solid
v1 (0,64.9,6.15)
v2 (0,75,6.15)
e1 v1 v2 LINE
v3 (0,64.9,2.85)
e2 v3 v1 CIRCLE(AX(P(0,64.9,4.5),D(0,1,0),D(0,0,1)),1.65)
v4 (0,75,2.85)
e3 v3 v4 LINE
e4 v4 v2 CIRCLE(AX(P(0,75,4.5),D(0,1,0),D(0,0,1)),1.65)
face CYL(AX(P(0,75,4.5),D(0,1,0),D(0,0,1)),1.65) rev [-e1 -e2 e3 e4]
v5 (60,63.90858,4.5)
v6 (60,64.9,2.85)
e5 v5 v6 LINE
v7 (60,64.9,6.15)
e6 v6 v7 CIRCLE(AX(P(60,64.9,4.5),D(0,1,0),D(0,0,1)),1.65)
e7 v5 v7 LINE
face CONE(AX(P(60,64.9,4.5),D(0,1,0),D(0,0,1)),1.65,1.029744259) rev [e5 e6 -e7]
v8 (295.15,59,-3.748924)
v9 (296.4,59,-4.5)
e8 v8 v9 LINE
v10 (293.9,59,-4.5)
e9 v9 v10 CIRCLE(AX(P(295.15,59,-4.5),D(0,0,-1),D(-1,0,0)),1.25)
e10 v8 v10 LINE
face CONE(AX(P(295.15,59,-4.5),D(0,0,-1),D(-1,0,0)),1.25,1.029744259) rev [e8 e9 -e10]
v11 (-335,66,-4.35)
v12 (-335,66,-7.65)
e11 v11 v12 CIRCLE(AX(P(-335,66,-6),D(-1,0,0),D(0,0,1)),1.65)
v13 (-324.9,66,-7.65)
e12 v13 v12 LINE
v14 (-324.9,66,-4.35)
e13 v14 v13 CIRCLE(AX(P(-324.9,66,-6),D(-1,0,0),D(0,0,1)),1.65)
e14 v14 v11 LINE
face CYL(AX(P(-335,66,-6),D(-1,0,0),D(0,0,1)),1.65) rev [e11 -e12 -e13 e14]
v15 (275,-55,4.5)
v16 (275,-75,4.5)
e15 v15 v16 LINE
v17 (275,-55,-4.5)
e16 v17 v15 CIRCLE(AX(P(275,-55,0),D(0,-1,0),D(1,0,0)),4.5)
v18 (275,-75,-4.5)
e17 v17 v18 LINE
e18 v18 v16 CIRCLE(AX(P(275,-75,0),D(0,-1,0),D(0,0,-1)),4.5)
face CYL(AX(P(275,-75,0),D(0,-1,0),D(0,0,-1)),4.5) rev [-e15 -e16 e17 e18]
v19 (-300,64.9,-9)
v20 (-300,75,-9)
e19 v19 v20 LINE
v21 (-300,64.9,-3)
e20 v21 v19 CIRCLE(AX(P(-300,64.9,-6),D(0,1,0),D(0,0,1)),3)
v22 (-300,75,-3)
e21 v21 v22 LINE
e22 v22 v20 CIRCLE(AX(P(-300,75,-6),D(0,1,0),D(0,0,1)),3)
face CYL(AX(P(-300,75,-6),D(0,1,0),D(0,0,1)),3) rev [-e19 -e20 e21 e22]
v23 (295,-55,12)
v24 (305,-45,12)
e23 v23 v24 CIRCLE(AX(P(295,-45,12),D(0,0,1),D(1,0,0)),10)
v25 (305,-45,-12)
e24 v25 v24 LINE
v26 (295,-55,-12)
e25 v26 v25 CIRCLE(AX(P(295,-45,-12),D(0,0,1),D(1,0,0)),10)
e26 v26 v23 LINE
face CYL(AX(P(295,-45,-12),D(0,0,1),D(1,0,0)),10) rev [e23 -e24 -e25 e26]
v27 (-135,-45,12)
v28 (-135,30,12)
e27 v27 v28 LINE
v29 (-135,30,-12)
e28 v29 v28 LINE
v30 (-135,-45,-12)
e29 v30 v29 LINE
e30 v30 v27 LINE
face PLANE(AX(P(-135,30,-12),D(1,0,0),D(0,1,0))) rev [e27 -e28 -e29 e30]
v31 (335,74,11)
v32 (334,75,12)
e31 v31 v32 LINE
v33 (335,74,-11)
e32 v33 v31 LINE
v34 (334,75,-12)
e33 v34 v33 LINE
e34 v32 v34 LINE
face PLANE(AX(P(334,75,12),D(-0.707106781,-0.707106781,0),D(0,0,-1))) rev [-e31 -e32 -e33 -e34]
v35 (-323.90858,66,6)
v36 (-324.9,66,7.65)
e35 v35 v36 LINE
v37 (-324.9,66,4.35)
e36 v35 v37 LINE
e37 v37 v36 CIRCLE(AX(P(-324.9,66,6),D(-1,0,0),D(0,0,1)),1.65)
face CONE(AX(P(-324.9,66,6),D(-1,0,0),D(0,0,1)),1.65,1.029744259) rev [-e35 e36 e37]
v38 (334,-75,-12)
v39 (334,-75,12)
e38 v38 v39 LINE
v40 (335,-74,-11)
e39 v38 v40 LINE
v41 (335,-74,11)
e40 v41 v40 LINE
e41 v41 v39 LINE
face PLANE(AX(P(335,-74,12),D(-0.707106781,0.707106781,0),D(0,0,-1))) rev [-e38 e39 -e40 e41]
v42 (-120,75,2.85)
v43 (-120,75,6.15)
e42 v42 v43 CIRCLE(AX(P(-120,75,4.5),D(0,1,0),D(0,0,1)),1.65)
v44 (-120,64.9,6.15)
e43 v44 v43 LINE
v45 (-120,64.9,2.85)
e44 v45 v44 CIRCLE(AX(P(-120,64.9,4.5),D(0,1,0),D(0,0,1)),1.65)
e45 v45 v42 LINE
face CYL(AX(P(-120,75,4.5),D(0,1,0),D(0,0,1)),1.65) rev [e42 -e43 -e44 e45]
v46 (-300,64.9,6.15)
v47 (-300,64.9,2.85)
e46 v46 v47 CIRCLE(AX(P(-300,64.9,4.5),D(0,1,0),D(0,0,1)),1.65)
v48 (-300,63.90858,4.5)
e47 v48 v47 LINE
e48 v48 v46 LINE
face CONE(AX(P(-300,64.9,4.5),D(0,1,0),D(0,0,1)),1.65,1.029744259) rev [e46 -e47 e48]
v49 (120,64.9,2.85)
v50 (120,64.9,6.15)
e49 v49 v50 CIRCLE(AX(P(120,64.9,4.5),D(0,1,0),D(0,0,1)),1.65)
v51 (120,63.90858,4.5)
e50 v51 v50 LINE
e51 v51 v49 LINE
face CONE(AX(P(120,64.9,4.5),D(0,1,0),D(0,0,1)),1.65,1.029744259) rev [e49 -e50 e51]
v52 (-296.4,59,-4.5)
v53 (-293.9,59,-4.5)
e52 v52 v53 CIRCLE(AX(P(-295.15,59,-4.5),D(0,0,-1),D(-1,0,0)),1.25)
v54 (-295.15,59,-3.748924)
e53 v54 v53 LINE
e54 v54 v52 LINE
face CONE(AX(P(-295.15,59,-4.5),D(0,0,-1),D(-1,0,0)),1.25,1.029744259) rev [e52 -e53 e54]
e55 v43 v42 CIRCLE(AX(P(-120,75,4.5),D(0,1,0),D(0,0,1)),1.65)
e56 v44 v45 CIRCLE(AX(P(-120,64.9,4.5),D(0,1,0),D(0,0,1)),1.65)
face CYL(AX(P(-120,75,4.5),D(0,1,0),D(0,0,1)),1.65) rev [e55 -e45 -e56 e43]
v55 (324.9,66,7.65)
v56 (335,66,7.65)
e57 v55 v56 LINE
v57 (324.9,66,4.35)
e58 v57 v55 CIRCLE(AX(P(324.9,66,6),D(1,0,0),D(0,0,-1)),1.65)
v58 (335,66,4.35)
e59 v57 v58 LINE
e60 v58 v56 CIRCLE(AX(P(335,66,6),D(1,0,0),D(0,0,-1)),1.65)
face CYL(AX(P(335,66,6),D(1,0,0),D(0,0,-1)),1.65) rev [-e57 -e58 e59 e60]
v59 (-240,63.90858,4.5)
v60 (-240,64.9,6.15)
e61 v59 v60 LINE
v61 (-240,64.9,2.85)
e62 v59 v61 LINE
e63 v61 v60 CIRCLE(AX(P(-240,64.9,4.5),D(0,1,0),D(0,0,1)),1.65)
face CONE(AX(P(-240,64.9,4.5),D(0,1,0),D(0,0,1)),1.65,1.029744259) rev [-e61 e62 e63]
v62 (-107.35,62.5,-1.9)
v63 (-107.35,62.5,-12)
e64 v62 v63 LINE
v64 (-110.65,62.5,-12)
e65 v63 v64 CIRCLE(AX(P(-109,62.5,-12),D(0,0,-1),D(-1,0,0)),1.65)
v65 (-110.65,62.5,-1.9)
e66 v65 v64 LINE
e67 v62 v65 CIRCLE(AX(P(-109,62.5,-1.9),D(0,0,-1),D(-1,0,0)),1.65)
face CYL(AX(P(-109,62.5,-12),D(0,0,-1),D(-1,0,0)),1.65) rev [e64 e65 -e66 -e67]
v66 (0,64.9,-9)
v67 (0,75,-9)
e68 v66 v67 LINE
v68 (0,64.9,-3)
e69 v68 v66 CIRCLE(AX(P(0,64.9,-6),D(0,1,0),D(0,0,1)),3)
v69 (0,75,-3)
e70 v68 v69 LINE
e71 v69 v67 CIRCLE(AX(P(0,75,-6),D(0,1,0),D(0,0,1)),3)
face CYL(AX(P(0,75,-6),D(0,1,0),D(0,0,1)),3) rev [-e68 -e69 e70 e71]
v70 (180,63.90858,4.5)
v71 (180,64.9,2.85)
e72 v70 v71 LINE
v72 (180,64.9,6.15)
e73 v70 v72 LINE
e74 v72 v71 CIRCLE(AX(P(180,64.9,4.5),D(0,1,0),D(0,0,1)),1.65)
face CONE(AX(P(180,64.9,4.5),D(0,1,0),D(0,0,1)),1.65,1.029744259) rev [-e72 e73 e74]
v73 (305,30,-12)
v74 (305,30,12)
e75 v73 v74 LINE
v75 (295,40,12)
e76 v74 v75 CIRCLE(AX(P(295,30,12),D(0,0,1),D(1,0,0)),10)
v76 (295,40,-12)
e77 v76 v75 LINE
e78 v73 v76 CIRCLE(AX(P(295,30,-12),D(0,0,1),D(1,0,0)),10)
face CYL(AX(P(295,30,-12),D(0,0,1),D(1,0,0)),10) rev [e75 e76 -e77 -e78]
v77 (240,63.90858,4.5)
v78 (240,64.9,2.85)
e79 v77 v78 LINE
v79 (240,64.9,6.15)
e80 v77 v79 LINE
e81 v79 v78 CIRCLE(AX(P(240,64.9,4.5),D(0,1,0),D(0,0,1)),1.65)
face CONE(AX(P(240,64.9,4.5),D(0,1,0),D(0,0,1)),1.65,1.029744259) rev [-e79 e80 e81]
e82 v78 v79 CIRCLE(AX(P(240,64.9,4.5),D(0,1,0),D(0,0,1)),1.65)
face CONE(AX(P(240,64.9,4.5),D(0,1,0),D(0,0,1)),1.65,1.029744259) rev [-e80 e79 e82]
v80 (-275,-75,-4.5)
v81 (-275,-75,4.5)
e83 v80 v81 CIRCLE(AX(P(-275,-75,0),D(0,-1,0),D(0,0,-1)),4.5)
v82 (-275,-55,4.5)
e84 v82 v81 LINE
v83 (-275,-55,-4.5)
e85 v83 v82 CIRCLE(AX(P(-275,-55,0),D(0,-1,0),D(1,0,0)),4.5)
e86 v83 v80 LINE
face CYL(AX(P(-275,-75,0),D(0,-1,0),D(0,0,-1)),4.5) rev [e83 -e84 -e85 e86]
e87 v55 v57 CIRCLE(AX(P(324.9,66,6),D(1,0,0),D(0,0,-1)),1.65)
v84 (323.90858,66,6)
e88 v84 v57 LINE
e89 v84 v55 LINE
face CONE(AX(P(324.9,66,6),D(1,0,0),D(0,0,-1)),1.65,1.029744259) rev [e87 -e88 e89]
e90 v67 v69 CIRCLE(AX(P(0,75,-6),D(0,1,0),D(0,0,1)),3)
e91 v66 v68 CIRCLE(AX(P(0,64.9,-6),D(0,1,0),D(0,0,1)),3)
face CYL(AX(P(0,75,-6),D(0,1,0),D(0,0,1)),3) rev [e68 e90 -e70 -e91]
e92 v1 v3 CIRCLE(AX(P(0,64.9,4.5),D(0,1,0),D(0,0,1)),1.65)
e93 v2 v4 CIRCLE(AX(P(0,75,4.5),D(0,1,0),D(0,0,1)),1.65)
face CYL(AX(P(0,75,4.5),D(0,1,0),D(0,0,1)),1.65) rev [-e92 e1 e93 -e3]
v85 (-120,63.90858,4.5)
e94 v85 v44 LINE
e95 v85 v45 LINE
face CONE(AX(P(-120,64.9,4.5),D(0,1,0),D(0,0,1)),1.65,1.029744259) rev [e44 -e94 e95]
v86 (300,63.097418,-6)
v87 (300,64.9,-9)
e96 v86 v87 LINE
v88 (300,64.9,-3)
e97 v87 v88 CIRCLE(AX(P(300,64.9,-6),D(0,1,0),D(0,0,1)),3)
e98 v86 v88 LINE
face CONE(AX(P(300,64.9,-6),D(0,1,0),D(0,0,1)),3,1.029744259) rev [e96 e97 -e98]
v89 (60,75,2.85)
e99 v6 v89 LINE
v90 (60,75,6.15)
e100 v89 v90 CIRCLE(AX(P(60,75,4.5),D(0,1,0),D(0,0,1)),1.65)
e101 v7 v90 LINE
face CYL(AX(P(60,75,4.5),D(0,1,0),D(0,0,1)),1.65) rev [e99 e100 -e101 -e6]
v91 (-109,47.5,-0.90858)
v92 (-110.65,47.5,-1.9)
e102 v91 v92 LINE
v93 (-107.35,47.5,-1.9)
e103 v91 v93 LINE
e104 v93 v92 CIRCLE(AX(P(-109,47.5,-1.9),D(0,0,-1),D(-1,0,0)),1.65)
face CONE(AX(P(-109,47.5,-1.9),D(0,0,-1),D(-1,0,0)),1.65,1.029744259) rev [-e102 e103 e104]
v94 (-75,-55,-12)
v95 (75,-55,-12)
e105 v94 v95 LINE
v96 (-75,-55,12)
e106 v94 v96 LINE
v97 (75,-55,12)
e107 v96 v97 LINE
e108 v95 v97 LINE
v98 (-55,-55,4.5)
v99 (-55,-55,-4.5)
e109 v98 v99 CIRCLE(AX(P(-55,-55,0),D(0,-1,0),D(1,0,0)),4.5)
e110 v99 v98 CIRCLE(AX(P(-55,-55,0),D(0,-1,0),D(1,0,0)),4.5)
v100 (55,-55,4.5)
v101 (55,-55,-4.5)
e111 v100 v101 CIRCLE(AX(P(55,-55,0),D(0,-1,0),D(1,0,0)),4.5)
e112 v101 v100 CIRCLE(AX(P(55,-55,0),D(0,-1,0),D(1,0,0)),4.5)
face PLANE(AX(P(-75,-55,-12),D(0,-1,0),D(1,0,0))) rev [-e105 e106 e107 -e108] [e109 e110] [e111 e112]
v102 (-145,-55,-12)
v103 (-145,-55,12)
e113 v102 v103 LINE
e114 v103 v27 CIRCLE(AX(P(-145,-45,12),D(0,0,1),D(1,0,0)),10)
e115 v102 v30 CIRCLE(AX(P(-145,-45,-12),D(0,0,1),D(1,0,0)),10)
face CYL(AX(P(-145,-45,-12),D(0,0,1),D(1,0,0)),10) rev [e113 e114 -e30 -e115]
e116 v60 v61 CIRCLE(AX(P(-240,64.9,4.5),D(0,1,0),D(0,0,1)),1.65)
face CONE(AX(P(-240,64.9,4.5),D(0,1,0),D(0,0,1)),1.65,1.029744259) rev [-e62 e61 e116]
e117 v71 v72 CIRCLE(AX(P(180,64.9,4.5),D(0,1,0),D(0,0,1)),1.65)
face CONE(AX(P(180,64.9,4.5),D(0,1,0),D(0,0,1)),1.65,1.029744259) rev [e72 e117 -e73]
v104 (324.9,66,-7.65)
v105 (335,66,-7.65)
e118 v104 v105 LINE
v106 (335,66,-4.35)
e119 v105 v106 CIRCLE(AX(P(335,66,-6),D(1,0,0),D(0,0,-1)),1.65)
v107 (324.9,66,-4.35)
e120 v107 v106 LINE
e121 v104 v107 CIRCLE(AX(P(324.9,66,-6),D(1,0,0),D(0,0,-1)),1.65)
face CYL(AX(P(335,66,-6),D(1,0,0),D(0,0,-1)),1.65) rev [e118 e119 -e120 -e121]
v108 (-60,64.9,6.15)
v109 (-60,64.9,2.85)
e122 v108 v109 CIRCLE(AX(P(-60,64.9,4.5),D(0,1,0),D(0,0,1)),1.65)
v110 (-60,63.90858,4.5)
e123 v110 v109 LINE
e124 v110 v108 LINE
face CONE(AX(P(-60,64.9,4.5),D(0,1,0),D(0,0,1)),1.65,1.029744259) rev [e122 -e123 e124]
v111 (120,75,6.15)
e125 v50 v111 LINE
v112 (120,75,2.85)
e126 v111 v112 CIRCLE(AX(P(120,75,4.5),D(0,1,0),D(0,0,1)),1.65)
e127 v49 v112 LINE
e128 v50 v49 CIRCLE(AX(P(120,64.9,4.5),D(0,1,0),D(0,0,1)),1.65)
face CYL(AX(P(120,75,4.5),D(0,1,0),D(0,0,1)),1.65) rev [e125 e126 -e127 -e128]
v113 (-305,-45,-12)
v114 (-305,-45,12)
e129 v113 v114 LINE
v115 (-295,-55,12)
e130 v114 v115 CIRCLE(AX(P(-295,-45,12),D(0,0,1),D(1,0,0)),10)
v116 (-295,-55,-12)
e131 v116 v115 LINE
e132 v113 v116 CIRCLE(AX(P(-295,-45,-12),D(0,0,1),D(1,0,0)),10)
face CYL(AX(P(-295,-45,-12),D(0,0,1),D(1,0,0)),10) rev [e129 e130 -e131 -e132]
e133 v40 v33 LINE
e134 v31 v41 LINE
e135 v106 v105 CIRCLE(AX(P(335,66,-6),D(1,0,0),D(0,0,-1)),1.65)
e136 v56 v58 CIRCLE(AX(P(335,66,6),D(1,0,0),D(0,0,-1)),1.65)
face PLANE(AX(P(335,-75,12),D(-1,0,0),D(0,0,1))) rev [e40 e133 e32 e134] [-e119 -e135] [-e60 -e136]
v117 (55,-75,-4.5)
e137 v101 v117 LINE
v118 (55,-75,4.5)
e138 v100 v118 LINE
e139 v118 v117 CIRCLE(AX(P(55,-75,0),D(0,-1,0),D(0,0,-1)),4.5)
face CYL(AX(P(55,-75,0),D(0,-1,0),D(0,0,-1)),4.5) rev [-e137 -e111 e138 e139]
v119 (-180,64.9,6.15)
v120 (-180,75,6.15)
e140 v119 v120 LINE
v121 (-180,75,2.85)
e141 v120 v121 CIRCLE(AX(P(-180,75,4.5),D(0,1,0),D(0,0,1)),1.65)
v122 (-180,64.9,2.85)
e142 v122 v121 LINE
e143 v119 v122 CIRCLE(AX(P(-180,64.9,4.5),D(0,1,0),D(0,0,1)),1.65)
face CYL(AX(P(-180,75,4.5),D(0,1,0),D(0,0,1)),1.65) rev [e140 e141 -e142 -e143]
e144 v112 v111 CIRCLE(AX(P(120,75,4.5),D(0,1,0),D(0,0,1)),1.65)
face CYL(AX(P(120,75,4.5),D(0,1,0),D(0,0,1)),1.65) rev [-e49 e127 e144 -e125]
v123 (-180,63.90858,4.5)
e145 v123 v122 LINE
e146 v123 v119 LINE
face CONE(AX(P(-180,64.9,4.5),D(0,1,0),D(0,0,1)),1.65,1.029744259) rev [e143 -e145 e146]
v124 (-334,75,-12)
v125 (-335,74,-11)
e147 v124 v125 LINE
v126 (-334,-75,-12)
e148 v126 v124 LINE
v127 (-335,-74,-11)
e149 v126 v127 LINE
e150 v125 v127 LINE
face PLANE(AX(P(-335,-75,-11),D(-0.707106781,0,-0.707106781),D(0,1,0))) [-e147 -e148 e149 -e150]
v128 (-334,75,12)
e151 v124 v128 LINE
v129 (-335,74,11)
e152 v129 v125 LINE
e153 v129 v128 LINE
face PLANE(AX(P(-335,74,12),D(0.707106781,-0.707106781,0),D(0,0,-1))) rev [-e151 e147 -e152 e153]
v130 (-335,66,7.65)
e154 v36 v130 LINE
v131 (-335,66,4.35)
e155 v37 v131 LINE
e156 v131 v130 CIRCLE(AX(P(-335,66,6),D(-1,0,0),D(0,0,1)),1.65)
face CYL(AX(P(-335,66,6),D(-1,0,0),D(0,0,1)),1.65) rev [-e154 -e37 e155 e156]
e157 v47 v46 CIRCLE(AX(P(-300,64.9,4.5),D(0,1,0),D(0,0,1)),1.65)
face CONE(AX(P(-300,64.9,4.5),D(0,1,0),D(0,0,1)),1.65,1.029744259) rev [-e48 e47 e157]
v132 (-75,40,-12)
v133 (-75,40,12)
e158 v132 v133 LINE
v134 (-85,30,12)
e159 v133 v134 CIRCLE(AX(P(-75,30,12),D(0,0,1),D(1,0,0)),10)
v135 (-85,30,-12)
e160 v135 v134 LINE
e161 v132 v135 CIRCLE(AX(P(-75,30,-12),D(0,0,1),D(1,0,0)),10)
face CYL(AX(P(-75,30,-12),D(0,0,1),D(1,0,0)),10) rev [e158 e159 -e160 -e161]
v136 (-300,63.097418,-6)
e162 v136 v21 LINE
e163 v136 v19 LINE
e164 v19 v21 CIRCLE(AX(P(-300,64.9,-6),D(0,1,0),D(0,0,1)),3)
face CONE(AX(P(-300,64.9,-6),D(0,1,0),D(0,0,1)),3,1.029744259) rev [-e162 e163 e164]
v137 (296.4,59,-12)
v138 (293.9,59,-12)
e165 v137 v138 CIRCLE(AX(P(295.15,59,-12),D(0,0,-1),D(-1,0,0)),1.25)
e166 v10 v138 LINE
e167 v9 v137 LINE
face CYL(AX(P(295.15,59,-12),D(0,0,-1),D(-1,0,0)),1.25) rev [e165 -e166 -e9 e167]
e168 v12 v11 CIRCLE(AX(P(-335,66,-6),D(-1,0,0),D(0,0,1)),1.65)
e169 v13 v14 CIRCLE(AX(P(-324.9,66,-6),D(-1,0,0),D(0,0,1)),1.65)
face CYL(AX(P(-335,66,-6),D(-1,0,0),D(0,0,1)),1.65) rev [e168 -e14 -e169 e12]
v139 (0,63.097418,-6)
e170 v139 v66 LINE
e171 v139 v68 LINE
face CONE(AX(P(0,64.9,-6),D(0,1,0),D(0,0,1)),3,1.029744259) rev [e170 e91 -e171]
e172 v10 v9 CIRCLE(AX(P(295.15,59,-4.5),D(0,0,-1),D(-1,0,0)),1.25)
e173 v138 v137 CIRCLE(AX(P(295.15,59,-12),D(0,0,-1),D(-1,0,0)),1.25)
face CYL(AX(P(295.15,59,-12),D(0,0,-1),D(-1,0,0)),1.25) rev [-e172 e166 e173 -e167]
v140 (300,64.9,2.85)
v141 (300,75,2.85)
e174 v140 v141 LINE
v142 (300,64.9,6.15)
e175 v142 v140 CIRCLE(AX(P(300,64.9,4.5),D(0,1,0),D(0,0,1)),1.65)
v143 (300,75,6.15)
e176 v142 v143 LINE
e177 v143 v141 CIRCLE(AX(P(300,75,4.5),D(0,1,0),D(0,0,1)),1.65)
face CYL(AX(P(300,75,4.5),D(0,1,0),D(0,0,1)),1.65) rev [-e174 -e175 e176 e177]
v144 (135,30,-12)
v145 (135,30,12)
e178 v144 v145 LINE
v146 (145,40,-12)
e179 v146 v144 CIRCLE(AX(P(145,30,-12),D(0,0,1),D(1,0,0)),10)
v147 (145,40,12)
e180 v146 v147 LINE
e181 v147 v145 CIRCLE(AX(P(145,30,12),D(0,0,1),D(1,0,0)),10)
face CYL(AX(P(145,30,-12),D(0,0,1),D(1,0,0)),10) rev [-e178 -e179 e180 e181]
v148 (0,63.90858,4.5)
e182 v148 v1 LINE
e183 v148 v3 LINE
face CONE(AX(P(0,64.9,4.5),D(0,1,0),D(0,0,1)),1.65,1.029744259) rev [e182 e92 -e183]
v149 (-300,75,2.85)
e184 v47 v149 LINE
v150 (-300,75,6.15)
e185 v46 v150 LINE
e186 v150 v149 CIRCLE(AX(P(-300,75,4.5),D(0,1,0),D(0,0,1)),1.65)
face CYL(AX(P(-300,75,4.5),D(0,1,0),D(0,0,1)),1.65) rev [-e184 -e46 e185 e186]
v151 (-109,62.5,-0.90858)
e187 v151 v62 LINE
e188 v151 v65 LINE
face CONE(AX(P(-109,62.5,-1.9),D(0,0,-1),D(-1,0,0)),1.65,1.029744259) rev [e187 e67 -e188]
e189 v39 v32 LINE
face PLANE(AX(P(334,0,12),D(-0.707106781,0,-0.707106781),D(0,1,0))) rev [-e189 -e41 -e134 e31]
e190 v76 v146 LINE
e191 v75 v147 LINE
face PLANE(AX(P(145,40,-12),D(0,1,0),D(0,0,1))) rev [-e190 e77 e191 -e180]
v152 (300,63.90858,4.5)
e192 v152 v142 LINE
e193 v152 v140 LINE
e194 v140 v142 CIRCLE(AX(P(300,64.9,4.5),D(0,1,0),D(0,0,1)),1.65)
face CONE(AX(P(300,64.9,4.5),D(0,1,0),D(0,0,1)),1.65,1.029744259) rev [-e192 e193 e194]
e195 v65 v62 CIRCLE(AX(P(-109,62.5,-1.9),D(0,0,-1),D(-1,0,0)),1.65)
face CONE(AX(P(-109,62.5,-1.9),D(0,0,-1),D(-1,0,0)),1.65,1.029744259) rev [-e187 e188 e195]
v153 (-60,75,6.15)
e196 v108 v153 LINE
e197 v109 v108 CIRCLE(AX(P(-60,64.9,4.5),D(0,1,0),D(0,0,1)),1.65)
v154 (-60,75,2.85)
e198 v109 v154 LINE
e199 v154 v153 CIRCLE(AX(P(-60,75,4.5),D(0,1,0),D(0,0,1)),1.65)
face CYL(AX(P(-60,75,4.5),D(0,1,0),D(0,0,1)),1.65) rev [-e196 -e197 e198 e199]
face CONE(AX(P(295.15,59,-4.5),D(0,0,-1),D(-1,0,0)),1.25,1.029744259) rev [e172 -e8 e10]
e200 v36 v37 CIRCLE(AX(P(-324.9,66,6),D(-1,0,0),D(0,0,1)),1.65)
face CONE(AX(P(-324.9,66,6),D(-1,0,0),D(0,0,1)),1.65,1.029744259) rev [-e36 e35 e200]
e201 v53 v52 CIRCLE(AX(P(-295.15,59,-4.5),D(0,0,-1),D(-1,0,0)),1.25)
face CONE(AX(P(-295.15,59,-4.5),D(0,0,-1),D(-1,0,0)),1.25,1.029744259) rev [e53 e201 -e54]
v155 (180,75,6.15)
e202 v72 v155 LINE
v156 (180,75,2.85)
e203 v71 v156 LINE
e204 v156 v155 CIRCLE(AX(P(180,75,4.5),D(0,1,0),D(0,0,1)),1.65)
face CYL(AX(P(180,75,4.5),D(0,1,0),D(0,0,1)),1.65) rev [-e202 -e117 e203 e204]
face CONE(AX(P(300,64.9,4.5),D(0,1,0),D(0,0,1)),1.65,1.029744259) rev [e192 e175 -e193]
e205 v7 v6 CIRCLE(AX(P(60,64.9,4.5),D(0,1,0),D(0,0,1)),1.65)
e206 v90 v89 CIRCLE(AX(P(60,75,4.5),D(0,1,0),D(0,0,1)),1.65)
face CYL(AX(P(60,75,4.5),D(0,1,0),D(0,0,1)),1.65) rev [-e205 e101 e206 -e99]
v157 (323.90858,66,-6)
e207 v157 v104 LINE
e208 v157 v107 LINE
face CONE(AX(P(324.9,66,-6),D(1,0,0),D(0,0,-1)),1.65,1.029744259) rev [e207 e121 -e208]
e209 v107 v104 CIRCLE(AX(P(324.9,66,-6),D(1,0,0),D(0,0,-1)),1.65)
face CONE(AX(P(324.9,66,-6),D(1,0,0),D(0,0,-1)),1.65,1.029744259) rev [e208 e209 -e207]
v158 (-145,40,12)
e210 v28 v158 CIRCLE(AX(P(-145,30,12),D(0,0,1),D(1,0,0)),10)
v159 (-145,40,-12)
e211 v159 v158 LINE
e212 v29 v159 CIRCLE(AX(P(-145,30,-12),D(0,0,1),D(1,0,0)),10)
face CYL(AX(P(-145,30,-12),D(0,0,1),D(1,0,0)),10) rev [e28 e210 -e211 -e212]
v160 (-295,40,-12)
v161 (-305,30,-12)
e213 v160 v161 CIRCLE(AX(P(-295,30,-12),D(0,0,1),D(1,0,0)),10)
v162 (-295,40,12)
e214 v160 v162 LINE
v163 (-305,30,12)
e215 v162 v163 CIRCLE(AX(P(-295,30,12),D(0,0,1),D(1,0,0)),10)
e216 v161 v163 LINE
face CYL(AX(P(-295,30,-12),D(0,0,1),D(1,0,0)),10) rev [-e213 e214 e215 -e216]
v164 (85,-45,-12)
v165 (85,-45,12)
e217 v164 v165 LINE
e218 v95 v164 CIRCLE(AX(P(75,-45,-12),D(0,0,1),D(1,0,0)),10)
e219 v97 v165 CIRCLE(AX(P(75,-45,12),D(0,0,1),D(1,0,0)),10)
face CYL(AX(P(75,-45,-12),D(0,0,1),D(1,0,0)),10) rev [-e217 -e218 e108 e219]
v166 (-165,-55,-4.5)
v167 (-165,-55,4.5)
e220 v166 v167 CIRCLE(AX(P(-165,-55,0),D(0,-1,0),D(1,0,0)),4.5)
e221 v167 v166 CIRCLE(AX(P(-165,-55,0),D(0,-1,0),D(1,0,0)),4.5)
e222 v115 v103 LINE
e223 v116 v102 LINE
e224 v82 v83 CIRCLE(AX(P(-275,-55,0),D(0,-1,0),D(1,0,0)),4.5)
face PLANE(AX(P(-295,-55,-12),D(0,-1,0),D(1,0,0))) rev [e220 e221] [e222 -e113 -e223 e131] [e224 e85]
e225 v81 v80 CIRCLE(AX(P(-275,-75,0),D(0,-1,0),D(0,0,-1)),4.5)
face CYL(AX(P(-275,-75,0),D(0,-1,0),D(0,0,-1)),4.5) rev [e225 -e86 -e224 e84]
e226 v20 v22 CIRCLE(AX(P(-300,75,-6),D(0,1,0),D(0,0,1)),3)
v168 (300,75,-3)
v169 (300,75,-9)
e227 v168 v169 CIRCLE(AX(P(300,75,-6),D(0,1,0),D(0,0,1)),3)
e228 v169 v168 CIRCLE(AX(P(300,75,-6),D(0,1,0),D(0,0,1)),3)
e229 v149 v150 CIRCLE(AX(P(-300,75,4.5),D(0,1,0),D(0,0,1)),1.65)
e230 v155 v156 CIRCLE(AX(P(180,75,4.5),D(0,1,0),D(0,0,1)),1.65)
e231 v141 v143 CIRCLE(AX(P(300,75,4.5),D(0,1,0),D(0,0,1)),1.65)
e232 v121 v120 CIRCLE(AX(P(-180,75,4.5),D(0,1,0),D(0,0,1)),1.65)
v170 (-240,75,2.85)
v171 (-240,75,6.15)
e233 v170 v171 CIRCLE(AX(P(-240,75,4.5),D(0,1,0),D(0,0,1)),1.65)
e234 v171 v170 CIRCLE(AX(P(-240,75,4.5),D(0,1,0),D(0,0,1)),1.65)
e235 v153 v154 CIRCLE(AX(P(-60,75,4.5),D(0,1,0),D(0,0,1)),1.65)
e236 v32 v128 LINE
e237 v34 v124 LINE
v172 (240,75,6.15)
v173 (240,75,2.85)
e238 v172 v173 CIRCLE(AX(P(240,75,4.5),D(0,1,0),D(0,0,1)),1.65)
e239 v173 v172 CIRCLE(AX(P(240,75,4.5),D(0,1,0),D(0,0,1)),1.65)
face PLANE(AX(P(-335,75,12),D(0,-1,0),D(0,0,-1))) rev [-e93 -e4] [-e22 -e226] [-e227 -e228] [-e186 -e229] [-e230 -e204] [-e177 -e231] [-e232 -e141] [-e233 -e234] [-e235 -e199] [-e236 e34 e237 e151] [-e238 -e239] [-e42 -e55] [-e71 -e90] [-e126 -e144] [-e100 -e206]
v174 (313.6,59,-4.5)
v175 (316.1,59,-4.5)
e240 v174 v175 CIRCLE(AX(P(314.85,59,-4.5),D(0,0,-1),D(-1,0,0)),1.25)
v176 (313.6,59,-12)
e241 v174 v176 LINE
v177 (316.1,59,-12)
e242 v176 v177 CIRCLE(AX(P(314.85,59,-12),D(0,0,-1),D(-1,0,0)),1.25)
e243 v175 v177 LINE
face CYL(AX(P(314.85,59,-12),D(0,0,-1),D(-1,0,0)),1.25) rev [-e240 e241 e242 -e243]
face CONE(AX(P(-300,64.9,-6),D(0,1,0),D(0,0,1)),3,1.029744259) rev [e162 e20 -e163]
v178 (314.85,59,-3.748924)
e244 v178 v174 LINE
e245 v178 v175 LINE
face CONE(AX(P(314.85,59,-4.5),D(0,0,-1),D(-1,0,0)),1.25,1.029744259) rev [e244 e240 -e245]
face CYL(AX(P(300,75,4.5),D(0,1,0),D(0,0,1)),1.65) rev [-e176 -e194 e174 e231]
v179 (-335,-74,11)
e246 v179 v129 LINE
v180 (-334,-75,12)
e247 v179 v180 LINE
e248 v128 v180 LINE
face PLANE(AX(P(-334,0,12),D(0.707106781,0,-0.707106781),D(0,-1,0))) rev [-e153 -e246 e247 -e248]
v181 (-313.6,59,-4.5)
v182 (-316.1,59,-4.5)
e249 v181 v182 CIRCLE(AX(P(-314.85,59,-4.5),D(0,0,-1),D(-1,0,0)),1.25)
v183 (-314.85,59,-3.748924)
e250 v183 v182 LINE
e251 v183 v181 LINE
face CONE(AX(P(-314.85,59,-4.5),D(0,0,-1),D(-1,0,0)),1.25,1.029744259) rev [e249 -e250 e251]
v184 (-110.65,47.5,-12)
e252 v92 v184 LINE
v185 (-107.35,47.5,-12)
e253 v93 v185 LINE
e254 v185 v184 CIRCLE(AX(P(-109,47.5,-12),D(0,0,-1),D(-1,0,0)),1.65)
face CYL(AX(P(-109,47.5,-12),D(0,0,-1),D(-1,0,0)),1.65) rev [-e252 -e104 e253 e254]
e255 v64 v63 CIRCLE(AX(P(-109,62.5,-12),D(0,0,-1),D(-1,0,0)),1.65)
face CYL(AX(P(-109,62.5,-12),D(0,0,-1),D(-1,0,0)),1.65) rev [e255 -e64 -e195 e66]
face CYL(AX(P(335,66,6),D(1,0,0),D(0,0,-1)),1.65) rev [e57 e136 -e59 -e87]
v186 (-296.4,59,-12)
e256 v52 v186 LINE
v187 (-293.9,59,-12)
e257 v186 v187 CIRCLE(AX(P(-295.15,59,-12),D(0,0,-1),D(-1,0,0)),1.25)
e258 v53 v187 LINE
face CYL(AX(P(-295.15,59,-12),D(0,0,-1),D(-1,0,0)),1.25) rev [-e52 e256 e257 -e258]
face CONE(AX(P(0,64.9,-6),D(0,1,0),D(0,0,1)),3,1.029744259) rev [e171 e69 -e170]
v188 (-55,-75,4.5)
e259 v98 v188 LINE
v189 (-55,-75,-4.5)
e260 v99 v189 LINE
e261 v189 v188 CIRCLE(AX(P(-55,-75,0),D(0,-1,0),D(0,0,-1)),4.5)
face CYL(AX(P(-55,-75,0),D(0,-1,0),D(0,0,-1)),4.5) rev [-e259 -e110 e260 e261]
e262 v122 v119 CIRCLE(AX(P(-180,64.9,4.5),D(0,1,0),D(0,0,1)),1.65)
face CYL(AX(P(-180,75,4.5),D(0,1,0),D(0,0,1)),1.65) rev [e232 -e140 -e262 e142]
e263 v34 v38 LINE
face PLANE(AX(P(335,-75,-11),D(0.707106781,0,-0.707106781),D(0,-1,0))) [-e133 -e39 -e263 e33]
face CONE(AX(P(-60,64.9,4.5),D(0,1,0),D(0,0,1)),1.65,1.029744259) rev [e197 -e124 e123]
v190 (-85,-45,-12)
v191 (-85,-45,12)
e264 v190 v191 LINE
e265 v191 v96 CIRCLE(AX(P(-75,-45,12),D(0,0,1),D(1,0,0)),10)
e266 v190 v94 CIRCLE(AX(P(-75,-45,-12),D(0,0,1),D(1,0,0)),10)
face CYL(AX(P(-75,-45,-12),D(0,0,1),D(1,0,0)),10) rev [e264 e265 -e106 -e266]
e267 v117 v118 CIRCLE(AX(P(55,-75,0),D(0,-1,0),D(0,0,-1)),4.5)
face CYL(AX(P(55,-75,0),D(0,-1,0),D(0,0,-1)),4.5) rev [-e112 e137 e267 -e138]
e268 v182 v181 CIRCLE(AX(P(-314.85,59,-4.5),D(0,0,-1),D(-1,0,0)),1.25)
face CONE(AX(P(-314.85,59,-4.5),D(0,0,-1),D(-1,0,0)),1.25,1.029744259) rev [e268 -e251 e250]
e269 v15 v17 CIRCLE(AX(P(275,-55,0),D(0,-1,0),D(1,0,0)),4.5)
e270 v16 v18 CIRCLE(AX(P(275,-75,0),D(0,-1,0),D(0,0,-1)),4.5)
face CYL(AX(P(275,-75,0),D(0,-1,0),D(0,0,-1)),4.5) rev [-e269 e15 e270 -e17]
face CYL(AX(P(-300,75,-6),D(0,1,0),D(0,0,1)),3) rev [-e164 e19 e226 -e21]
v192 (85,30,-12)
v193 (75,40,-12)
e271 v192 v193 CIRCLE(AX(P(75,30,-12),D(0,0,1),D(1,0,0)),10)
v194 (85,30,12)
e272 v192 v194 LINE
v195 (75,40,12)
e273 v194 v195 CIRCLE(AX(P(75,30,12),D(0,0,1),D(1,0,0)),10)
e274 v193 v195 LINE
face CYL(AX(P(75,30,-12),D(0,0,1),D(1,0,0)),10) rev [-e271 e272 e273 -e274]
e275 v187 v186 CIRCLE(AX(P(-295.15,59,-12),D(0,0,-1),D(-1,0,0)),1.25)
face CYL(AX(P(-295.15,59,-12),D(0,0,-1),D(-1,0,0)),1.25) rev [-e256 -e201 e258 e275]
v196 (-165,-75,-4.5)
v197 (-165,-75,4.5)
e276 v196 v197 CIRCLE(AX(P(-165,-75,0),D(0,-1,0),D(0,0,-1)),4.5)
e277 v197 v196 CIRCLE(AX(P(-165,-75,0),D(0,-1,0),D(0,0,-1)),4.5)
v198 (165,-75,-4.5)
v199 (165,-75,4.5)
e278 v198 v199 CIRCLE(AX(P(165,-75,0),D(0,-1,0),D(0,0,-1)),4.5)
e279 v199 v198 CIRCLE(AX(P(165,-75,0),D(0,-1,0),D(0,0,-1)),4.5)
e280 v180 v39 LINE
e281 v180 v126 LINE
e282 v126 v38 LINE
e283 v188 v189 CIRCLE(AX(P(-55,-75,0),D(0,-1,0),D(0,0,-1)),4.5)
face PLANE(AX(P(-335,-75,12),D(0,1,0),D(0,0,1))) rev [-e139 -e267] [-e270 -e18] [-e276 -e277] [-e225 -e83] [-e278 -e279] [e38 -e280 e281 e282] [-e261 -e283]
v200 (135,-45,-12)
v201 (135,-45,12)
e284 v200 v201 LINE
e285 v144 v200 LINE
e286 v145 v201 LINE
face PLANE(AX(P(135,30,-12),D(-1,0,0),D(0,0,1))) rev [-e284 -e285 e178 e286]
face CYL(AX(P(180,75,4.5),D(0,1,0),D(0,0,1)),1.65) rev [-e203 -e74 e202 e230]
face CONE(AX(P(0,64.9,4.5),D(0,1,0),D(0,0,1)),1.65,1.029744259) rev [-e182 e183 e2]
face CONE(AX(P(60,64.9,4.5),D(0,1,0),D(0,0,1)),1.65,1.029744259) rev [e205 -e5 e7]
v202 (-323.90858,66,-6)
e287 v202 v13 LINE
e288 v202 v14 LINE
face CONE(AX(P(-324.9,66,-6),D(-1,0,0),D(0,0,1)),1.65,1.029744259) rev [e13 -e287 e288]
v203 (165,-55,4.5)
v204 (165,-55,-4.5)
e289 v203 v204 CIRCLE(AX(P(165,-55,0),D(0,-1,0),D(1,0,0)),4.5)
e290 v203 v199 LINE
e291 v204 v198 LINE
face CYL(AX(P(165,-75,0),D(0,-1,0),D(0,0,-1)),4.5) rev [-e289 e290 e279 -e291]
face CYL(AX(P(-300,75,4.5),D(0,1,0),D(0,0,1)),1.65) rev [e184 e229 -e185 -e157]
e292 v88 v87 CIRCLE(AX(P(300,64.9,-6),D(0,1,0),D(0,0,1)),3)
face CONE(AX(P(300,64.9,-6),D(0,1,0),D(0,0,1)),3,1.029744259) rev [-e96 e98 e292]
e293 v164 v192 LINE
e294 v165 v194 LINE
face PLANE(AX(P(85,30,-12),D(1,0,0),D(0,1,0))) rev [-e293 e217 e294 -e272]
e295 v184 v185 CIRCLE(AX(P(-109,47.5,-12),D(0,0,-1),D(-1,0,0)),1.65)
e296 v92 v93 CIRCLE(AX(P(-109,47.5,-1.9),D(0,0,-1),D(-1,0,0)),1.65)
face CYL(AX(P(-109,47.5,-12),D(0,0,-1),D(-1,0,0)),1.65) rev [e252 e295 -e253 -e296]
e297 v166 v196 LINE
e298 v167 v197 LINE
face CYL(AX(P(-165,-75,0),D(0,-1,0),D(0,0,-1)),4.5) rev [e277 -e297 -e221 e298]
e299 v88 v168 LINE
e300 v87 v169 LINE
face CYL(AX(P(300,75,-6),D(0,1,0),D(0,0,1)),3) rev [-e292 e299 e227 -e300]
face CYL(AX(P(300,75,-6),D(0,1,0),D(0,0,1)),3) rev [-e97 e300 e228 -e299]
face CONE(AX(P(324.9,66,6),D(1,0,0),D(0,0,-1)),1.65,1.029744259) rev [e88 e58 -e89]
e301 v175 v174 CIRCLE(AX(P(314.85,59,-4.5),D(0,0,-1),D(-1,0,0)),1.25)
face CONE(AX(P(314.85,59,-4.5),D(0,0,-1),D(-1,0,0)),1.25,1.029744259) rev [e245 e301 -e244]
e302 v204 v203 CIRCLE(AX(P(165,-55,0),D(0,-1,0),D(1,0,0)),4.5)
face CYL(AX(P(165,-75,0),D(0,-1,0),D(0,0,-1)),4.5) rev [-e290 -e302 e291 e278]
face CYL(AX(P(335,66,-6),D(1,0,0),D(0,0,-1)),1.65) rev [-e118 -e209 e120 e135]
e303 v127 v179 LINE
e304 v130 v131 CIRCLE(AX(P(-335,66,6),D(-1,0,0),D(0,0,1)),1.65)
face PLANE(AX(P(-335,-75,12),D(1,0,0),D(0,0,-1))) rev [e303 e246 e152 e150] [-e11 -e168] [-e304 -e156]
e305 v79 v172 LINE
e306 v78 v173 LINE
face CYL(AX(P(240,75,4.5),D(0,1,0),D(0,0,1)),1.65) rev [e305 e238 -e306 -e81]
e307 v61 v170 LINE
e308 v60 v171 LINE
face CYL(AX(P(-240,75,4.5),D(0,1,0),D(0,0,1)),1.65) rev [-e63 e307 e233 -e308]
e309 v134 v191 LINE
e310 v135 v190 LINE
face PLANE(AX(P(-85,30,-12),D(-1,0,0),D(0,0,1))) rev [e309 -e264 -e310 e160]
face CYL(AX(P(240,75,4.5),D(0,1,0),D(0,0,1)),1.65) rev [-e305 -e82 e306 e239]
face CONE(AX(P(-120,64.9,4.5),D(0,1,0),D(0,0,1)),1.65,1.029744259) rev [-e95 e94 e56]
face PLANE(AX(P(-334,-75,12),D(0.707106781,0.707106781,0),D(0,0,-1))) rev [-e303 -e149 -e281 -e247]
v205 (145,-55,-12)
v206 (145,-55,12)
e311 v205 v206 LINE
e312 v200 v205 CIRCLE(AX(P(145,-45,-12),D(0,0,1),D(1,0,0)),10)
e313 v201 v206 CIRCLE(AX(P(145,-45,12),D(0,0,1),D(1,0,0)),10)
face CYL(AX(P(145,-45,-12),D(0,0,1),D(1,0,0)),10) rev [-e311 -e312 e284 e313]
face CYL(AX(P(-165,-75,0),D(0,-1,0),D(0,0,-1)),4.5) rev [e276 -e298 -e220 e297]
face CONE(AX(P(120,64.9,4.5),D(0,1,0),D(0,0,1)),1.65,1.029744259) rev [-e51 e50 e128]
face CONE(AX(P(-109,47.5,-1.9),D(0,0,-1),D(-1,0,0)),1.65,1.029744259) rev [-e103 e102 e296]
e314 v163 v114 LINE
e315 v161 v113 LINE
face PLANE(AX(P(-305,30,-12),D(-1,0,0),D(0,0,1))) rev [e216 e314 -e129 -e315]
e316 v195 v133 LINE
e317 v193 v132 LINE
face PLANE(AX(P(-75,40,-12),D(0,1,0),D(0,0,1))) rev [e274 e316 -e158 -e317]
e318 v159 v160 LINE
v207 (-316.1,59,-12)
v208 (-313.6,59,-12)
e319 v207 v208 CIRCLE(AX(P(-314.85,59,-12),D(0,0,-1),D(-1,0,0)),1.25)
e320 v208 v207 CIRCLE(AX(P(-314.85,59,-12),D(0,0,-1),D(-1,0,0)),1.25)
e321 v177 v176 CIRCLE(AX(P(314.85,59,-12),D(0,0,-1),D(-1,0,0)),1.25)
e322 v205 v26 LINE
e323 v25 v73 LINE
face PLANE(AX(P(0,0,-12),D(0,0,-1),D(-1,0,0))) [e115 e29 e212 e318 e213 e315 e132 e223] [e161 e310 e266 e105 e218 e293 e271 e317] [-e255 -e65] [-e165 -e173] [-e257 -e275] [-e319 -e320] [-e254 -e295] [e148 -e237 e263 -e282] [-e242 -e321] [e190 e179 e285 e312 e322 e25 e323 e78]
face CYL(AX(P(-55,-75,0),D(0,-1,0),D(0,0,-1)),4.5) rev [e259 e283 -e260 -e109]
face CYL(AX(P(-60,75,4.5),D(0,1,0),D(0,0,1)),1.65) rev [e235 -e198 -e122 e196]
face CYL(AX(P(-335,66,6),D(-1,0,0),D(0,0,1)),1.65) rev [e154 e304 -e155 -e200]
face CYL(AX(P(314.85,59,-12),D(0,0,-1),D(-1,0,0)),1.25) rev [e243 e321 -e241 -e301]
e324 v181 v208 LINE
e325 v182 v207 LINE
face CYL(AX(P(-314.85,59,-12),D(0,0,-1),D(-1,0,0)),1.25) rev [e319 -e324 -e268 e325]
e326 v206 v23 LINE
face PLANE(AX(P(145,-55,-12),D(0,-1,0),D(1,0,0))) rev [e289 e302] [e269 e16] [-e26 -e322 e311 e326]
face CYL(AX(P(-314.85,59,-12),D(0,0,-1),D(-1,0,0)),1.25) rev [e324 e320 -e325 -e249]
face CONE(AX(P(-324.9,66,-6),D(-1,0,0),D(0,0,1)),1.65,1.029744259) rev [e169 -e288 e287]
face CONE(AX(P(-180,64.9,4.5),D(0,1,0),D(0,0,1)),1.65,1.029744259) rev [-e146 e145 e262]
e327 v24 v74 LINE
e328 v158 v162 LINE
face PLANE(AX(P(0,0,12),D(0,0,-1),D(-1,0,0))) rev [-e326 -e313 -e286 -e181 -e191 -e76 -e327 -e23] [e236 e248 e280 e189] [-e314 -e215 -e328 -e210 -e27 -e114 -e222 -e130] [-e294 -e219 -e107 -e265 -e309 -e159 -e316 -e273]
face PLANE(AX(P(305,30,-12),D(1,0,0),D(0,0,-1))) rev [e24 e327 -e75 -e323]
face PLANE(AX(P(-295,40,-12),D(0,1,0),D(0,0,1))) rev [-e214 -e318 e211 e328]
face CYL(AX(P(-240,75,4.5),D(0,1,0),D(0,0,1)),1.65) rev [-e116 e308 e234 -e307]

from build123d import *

# Parameters (mm, degrees)
SKETCH1_W                     = 670
SKETCH1_H                     = 150
BOSS_EXTRUDE1_DEPTH           = 12
CUT_EXTRUDE1_DEPTH            = 345.13078909
M8_CLEARANCE_HOLE1_D          = 9
M8_CLEARANCE_HOLE1_DEPTH      = 20
M4_TAPPED_HOLE1_D             = 3.3
M4_TAPPED_HOLE1_DEPTH         = 10.1
M4_TAPPED_HOLE1_TIP           = 0.991420021
SIZE_MM_BLIND_PIN_HOLE1_D     = 6
SIZE_MM_BLIND_PIN_HOLE1_DEPTH = 10.1
SIZE_MM_BLIND_PIN_HOLE1_TIP   = 1.802581857
CHAMFER1_SIZE                 = 1
M4_TAPPED_HOLE2_D             = 3.3
M4_TAPPED_HOLE2_DEPTH         = 10.1
M4_TAPPED_HOLE2_TIP           = 0.991420021
M4_TAPPED_HOLE3_D             = 3.3
M4_TAPPED_HOLE3_DEPTH         = 10.1
M4_TAPPED_HOLE3_TIP           = 0.991420021
M3_TAPPED_HOLE1_D             = 2.5
M3_TAPPED_HOLE1_DEPTH         = 7.5
M3_TAPPED_HOLE1_TIP           = 0.751075774
M4_TAPPED_HOLE4_D             = 3.3
M4_TAPPED_HOLE4_DEPTH         = 10.1
M4_TAPPED_HOLE4_TIP           = 0.991420021


with BuildPart() as part:
    # Sketch1 → Boss-Extrude1 (new, symmetric)
    with BuildSketch(Plane.XY):
        Rectangle(SKETCH1_W, SKETCH1_H)
    extrude(amount=BOSS_EXTRUDE1_DEPTH, both=True)

    # Sketch2 → Cut-Extrude1 (cut, through all)
    with BuildSketch(Plane.XY.offset(12)):
        with BuildLine():
            Line((-295, 40), (-145, 40))
            ThreePointArc((-145, 40), (-137.928932188, 37.071067812), (-135, 30))
            Line((-135, 30), (-135, -45))
            ThreePointArc((-135, -45), (-137.928932188, -52.071067812), (-145, -55))
            Line((-145, -55), (-295, -55))
            ThreePointArc((-295, -55), (-302.071067812, -52.071067812), (-305, -45))
            Line((-305, -45), (-305, 30))
            ThreePointArc((-305, 30), (-302.071067812, 37.071067812), (-295, 40))
        make_face()
        with BuildLine():
            Line((-75, 40), (75, 40))
            ThreePointArc((75, 40), (82.071067812, 37.071067812), (85, 30))
            Line((85, 30), (85, -45))
            ThreePointArc((85, -45), (82.071067812, -52.071067812), (75, -55))
            Line((75, -55), (-75, -55))
            ThreePointArc((-75, -55), (-82.071067812, -52.071067812), (-85, -45))
            Line((-85, -45), (-85, 30))
            ThreePointArc((-85, 30), (-82.071067812, 37.071067812), (-75, 40))
        make_face()
        with BuildLine():
            Line((145, 40), (295, 40))
            ThreePointArc((295, 40), (302.071067812, 37.071067812), (305, 30))
            Line((305, 30), (305, -45))
            ThreePointArc((305, -45), (302.071067812, -52.071067812), (295, -55))
            Line((295, -55), (145, -55))
            ThreePointArc((145, -55), (137.928932188, -52.071067812), (135, -45))
            Line((135, -45), (135, 30))
            ThreePointArc((135, 30), (137.928932188, 37.071067812), (145, 40))
        make_face()
    extrude(amount=-CUT_EXTRUDE1_DEPTH, mode=Mode.SUBTRACT)

    # M8 Clearance Hole1
    with Locations(Plane(origin=(0, -75, 0), x_dir=(-1, 0, 0), z_dir=(0, -1, 0))):
        with Locations((-275, 0), (275, 0), (165, 0), (55, 0), (-55, 0), (-165, 0)):
            Hole(M8_CLEARANCE_HOLE1_D / 2, depth=M8_CLEARANCE_HOLE1_DEPTH)

    # M4 Tapped Hole1
    with Locations(Plane(origin=(0, 75, 0), x_dir=(1, 0, 0), z_dir=(0, 1, 0))):
        with Locations((-300, -4.5), (-240, -4.5), (-180, -4.5), (-120, -4.5), (-60, -4.5), (0, -4.5), (60, -4.5), (120, -4.5), (180, -4.5), (240, -4.5), (300, -4.5)):
            Hole(M4_TAPPED_HOLE1_D / 2, depth=M4_TAPPED_HOLE1_DEPTH)
            with Locations((0, 0, -(M4_TAPPED_HOLE1_DEPTH + M4_TAPPED_HOLE1_TIP / 2))):  # 118° drill point
                Cone(0, M4_TAPPED_HOLE1_D / 2, M4_TAPPED_HOLE1_TIP, mode=Mode.SUBTRACT)

    # Size mm Blind Pin Hole1
    with Locations(Plane(origin=(0, 75, 0), x_dir=(1, 0, 0), z_dir=(0, 1, 0))):
        with Locations((300, 6), (-300, 6), (0, 6)):
            Hole(SIZE_MM_BLIND_PIN_HOLE1_D / 2, depth=SIZE_MM_BLIND_PIN_HOLE1_DEPTH)
            with Locations((0, 0, -(SIZE_MM_BLIND_PIN_HOLE1_DEPTH + SIZE_MM_BLIND_PIN_HOLE1_TIP / 2))):  # 118° drill point
                Cone(0, SIZE_MM_BLIND_PIN_HOLE1_D / 2, SIZE_MM_BLIND_PIN_HOLE1_TIP, mode=Mode.SUBTRACT)

    # Chamfer1
    chamfer1_edges = [part.edges().sort_by_distance(p)[0] for p in [
        (-335, 0, 12),
        (335, 0, 12),
        (-335, 0, -12),
        (335, 0, -12),
        (335, -75, 0),
        (-335, -75, 0),
        (-335, 75, 0),
        (335, 75, 0),
    ]]
    chamfer(chamfer1_edges, length=CHAMFER1_SIZE)

    # M4 Tapped Hole2
    with Locations(Plane(origin=(335, 0, 0), x_dir=(0, 0, -1), z_dir=(1, 0, 0))):
        with Locations((6, 66), (-6, 66)):
            Hole(M4_TAPPED_HOLE2_D / 2, depth=M4_TAPPED_HOLE2_DEPTH)
            with Locations((0, 0, -(M4_TAPPED_HOLE2_DEPTH + M4_TAPPED_HOLE2_TIP / 2))):  # 118° drill point
                Cone(0, M4_TAPPED_HOLE2_D / 2, M4_TAPPED_HOLE2_TIP, mode=Mode.SUBTRACT)

    # M4 Tapped Hole3
    with Locations(Plane.ZY.offset(335)):
        with Locations((-6, 66), (6, 66)):
            Hole(M4_TAPPED_HOLE3_D / 2, depth=M4_TAPPED_HOLE3_DEPTH)
            with Locations((0, 0, -(M4_TAPPED_HOLE3_DEPTH + M4_TAPPED_HOLE3_TIP / 2))):  # 118° drill point
                Cone(0, M4_TAPPED_HOLE3_D / 2, M4_TAPPED_HOLE3_TIP, mode=Mode.SUBTRACT)

    # M3 Tapped Hole1
    with Locations(Plane(origin=(0, 0, -12), x_dir=(1, 0, 0), z_dir=(0, 0, -1))):
        with Locations((314.85, -59), (-314.85, -59), (-295.15, -59), (295.15, -59)):
            Hole(M3_TAPPED_HOLE1_D / 2, depth=M3_TAPPED_HOLE1_DEPTH)
            with Locations((0, 0, -(M3_TAPPED_HOLE1_DEPTH + M3_TAPPED_HOLE1_TIP / 2))):  # 118° drill point
                Cone(0, M3_TAPPED_HOLE1_D / 2, M3_TAPPED_HOLE1_TIP, mode=Mode.SUBTRACT)

    # M4 Tapped Hole4
    with Locations(Plane(origin=(0, 0, -12), x_dir=(-1, 0, 0), z_dir=(0, 0, -1))):
        with Locations((109, 62.5), (109, 47.5)):
            Hole(M4_TAPPED_HOLE4_D / 2, depth=M4_TAPPED_HOLE4_DEPTH)
            with Locations((0, 0, -(M4_TAPPED_HOLE4_DEPTH + M4_TAPPED_HOLE4_TIP / 2))):  # 118° drill point
                Cone(0, M4_TAPPED_HOLE4_D / 2, M4_TAPPED_HOLE4_TIP, mode=Mode.SUBTRACT)


solid = part.part
